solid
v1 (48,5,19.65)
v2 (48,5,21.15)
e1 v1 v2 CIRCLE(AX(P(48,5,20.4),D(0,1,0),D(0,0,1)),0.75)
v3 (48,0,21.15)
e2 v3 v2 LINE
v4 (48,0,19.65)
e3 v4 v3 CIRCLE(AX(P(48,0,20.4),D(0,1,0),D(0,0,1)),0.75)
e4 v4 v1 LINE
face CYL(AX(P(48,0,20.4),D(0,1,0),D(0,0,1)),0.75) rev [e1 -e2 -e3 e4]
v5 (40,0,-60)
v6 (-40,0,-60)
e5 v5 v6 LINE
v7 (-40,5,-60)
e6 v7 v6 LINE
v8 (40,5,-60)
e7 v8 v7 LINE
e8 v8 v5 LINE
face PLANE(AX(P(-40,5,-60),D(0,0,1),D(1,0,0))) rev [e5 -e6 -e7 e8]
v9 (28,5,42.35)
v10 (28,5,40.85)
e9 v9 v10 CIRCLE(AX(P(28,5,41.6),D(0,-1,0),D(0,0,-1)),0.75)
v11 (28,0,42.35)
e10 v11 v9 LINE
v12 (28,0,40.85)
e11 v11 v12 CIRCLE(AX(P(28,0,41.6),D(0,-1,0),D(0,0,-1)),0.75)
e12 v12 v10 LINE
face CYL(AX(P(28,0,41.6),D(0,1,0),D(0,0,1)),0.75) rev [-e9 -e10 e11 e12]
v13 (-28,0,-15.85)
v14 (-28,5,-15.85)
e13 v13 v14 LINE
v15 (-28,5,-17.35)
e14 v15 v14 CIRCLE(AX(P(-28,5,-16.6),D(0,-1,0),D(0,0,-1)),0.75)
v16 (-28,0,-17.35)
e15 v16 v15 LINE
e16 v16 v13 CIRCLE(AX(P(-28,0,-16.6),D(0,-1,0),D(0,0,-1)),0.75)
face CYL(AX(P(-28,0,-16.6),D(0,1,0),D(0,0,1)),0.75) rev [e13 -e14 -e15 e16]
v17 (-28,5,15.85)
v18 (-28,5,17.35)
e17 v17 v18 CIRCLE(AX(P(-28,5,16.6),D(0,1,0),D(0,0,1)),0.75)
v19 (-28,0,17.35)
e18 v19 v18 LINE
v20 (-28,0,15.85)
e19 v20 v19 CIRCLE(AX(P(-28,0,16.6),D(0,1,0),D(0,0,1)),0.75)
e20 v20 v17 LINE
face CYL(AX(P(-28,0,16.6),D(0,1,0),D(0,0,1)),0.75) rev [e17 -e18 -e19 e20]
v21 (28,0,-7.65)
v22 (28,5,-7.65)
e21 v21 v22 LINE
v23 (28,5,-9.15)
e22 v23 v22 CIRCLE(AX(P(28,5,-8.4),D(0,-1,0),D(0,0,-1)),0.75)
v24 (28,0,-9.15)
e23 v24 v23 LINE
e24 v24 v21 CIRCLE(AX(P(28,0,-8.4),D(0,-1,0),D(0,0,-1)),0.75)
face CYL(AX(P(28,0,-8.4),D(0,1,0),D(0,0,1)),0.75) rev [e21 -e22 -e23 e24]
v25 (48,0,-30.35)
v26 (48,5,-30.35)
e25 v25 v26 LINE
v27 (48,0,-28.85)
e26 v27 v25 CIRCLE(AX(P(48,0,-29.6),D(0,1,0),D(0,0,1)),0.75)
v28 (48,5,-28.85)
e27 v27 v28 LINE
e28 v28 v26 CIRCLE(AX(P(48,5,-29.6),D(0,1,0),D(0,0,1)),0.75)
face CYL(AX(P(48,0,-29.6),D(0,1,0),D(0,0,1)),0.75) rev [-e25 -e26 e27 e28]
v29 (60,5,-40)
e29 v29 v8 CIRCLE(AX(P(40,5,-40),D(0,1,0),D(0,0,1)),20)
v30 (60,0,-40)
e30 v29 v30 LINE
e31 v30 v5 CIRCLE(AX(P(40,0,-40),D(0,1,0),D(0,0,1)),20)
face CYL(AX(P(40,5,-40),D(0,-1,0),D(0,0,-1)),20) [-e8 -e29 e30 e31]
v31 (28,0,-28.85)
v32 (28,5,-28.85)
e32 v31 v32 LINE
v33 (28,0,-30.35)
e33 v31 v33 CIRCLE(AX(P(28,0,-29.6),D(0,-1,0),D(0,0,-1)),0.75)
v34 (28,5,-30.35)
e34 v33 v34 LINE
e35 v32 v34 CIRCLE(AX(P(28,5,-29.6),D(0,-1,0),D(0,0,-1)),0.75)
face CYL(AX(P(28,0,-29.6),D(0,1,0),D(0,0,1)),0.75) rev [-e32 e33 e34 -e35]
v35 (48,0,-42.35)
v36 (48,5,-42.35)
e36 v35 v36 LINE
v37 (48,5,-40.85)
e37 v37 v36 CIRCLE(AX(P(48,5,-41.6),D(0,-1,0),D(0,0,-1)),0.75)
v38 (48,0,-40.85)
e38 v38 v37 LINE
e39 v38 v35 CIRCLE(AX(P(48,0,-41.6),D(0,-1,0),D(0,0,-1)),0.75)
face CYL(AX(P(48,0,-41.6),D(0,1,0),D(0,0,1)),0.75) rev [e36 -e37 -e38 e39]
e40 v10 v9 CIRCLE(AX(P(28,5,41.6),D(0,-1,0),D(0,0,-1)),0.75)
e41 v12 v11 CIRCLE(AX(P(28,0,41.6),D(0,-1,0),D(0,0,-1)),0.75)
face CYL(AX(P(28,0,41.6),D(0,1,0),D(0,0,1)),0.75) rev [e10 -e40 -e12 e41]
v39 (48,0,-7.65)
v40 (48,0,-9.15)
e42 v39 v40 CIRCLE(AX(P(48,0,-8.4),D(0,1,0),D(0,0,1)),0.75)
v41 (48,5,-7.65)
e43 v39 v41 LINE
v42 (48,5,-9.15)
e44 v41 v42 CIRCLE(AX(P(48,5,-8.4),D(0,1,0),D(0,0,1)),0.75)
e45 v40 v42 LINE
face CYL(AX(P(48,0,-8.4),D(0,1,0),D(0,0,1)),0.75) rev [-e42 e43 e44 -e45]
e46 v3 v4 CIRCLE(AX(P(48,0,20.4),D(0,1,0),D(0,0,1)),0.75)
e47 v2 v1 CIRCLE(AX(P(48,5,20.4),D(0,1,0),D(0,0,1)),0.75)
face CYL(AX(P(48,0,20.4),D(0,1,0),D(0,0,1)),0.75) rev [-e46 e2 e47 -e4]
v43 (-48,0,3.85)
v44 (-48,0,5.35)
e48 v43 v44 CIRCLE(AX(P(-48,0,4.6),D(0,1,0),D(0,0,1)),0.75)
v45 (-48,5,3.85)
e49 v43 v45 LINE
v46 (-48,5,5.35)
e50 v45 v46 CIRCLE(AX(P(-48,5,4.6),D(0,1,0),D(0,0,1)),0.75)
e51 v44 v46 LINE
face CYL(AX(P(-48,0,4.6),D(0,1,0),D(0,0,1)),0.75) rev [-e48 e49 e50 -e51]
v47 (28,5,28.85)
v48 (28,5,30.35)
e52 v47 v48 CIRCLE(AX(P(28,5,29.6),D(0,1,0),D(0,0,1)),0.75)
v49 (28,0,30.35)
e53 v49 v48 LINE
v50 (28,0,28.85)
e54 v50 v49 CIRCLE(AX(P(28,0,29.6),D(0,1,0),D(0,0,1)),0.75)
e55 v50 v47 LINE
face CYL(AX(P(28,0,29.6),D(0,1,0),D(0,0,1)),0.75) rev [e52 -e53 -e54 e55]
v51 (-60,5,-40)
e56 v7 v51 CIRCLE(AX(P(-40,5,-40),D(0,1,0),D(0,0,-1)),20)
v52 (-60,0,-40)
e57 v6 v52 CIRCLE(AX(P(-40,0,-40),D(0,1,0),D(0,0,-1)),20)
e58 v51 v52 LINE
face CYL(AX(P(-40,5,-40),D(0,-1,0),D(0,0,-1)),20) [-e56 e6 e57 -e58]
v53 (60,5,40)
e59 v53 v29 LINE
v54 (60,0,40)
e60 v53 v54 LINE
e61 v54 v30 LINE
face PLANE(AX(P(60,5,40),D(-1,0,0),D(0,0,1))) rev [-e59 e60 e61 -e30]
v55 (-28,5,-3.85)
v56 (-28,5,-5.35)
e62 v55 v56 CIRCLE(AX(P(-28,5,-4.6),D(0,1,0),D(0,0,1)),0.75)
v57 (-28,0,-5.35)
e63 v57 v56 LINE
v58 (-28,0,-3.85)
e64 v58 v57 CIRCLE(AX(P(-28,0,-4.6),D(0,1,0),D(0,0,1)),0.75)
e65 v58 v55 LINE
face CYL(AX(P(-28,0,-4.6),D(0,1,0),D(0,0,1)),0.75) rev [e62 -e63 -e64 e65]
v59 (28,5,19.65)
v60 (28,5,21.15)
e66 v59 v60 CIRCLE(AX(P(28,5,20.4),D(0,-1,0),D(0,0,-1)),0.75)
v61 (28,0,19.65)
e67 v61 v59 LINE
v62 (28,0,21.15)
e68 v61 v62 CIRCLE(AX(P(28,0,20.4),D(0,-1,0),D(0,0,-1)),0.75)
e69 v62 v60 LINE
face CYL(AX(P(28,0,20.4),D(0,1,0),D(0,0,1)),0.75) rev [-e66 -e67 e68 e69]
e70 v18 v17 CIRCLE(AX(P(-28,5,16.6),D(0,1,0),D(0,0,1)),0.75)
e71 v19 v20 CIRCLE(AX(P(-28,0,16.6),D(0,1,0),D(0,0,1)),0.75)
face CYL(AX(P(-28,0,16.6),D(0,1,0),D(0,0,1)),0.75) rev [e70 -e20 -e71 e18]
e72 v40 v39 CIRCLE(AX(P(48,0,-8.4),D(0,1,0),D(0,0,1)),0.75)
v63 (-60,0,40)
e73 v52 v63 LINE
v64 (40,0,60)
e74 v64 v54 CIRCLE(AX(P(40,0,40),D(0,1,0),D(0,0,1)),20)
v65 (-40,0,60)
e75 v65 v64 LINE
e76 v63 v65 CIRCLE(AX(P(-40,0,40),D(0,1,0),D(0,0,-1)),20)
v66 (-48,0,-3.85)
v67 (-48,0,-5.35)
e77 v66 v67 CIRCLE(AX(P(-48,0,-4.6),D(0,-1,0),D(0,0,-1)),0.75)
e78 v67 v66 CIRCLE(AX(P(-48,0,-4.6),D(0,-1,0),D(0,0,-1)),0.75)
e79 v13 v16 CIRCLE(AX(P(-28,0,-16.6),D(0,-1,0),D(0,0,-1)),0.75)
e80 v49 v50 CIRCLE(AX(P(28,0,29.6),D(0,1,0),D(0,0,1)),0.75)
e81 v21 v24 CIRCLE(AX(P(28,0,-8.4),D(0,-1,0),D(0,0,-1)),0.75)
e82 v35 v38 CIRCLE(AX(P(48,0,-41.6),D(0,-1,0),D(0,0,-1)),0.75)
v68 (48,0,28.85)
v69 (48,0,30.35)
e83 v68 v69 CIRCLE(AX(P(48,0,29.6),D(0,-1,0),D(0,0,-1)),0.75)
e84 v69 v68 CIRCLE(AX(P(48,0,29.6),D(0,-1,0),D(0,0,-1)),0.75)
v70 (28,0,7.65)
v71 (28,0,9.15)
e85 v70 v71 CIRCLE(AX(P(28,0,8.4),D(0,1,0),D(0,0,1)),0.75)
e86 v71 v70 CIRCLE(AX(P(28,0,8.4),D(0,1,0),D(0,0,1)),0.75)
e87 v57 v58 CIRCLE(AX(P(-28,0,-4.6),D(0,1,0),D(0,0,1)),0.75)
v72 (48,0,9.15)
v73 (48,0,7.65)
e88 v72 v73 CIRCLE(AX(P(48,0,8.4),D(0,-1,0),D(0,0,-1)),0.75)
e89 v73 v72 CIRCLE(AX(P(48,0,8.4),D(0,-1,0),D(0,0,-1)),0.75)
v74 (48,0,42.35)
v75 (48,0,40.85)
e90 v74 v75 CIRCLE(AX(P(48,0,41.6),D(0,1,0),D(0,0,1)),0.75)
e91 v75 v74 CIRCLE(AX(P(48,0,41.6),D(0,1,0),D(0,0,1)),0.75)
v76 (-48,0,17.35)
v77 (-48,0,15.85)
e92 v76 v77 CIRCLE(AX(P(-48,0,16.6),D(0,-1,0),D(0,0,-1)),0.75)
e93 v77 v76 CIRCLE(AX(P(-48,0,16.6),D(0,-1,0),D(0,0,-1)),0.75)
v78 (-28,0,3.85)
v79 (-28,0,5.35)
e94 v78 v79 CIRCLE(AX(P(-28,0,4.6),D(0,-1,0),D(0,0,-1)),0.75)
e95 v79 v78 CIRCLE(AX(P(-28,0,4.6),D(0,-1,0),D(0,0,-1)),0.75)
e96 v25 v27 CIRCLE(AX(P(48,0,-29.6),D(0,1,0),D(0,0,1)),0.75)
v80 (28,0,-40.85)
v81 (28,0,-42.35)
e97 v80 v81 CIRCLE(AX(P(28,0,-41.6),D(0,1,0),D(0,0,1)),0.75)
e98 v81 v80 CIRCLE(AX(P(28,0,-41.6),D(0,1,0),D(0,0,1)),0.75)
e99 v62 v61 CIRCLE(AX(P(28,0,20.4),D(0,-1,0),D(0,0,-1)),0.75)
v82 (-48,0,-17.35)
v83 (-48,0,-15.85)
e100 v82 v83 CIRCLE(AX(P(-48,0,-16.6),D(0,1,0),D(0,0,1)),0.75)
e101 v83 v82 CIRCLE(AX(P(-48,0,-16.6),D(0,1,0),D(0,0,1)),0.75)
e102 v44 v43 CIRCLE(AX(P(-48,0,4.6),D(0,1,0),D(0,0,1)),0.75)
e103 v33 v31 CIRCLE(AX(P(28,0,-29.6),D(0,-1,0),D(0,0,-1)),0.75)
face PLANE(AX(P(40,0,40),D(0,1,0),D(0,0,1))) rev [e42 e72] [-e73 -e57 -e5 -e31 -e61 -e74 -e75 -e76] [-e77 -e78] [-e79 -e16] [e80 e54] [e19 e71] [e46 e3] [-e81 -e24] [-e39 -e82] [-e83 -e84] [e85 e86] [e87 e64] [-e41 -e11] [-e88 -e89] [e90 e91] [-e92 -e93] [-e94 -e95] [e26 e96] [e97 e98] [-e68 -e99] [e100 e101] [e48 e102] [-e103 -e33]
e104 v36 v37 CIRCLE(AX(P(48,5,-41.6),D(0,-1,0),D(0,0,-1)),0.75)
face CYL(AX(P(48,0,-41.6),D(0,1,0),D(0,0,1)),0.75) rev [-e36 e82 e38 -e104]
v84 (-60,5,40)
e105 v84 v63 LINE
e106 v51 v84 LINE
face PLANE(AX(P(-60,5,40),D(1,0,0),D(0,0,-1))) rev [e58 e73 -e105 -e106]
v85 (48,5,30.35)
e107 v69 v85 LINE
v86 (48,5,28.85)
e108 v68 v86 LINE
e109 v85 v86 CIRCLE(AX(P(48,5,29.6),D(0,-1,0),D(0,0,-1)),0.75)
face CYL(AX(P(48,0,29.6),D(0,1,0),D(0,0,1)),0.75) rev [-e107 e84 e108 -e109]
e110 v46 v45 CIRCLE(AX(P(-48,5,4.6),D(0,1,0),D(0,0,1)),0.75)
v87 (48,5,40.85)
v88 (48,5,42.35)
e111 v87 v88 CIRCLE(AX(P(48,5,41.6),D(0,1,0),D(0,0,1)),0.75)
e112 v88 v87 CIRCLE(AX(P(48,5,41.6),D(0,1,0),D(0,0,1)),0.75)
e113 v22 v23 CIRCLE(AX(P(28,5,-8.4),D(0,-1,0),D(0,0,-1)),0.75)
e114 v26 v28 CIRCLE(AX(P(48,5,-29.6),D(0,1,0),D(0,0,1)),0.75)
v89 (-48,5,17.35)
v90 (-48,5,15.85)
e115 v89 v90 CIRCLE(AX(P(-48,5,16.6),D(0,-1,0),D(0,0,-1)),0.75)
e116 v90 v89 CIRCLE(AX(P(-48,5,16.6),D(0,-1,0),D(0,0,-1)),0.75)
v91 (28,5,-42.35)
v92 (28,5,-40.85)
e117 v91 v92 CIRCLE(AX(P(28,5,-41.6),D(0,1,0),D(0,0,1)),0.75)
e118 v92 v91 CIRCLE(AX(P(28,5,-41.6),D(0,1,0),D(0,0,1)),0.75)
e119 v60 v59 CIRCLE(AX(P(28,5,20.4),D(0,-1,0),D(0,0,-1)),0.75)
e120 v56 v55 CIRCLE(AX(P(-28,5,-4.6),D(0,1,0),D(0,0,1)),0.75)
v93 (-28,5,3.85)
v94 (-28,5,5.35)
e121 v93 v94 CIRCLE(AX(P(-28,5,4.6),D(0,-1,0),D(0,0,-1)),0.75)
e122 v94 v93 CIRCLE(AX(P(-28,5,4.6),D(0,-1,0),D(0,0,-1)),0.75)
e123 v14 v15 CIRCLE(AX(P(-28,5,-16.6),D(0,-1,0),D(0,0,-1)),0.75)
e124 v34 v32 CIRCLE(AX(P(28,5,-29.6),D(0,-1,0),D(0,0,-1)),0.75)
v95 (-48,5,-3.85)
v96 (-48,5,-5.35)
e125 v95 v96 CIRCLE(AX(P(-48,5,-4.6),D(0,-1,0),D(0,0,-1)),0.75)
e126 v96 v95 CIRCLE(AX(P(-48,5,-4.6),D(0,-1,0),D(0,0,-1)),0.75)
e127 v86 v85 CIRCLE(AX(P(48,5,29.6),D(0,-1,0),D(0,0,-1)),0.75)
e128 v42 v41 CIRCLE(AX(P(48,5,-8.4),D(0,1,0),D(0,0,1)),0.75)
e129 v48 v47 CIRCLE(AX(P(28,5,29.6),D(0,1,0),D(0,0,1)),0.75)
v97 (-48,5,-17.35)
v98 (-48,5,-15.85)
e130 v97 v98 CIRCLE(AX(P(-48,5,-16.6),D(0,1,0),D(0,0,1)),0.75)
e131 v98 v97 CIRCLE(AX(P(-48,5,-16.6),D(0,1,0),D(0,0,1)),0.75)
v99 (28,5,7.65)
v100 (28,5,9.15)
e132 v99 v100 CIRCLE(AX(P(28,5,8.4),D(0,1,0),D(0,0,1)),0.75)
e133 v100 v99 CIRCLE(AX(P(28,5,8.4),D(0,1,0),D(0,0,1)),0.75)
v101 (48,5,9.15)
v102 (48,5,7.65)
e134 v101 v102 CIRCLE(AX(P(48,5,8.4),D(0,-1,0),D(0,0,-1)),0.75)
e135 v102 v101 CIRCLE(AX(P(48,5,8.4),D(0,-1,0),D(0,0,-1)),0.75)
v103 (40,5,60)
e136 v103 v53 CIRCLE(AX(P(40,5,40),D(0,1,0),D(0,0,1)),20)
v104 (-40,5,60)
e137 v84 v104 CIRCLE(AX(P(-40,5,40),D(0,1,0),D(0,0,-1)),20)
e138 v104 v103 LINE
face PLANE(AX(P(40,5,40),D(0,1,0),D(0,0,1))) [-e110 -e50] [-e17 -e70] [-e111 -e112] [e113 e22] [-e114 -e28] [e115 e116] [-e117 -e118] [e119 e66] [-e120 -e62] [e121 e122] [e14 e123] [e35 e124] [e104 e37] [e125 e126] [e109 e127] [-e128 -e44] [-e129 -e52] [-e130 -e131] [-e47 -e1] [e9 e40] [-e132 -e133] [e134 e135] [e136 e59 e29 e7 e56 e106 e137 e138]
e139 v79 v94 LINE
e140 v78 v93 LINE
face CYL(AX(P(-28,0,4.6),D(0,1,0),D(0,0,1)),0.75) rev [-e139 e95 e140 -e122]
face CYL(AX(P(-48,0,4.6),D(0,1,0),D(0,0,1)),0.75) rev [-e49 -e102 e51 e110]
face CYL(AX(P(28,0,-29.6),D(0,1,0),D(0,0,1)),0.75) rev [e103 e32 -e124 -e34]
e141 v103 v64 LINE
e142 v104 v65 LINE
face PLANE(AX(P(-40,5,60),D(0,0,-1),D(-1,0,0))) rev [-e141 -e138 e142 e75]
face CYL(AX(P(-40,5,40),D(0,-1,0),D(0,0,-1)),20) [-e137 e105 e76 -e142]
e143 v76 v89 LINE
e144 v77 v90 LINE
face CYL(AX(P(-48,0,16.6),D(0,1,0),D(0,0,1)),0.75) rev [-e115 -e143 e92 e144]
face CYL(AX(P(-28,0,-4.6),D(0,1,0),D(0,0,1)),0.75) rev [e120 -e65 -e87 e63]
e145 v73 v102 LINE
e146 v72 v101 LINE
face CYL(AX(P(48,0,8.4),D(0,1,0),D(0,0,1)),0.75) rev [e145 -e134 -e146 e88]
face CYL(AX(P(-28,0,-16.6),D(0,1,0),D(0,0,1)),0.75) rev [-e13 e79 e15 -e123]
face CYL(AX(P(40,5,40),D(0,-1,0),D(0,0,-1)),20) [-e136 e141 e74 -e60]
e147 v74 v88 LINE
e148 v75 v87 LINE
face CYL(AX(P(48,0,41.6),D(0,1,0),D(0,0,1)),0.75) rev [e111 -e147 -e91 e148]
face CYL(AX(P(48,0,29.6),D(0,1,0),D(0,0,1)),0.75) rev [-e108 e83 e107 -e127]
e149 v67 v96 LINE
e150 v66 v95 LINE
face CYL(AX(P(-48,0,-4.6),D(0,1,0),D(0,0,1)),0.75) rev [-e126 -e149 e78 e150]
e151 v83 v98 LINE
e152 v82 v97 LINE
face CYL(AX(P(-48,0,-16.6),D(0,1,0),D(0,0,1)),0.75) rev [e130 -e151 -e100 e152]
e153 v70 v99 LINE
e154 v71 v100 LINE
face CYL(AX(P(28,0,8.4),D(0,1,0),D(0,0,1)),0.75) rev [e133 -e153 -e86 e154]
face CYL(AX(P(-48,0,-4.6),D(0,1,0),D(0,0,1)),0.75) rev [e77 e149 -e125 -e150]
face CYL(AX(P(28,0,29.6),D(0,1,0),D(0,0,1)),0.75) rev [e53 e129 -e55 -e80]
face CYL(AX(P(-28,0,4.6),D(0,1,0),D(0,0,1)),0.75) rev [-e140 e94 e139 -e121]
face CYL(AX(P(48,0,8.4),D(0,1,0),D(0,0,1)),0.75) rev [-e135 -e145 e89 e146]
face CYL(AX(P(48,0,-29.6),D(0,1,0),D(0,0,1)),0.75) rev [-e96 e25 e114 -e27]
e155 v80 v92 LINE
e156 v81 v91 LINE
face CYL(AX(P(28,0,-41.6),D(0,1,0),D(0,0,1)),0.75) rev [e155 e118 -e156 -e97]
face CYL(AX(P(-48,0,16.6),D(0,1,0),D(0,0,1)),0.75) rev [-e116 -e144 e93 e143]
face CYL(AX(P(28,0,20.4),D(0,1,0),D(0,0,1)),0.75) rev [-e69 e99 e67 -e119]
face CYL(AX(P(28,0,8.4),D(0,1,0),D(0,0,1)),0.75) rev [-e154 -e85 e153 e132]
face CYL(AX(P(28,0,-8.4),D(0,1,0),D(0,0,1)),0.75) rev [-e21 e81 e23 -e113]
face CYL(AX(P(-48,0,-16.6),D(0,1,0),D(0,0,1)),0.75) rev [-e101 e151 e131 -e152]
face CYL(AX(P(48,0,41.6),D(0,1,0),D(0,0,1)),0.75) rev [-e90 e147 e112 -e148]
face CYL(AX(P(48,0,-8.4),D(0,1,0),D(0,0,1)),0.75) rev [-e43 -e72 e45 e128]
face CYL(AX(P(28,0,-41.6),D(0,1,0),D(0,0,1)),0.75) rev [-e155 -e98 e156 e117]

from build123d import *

# Parameters (mm, degrees)
BOSS_EXTRUDE1_DEPTH = 5
SKETCH4_R           = 0.75
CUT_EXTRUDE1_DEPTH  = 86


with BuildPart() as part:
    # Sketch1 → Boss-Extrude1 (new body)
    with BuildSketch(Plane(origin=(0, 0, 0), x_dir=(1, 0, 0), z_dir=(0, 1, 0))):
        with BuildLine():
            Line((-40, -60), (40, -60))
            ThreePointArc((40, -60), (54.142135624, -54.142135624), (60, -40))
            Line((60, -40), (60, 40))
            ThreePointArc((60, 40), (54.142135624, 54.142135624), (40, 60))
            Line((40, 60), (-40, 60))
            ThreePointArc((-40, 60), (-54.142135624, 54.142135624), (-60, 40))
            Line((-60, 40), (-60, -40))
            ThreePointArc((-60, -40), (-54.142135624, -54.142135624), (-40, -60))
        make_face()
    extrude(amount=BOSS_EXTRUDE1_DEPTH)

    # Sketch4 → Cut-Extrude1 (cut, through all)
    with BuildSketch(Plane(origin=(0, 5, 0), x_dir=(1, 0, 0), z_dir=(0, 1, 0))):
        with Locations(Location((-48, 16.6, 0), (0, 0, 270))):
            Circle(SKETCH4_R)
        with Locations(Location((-28, 16.6, 0), (0, 0, 90))):
            Circle(SKETCH4_R)
        with Locations(Location((-48, 4.6, 0), (0, 0, 90))):
            Circle(SKETCH4_R)
        with Locations(Location((-28, 4.6, 0), (0, 0, 270))):
            Circle(SKETCH4_R)
        with Locations(Location((-28, -4.6, 0), (0, 0, 90))):
            Circle(SKETCH4_R)
        with Locations(Location((-48, -4.6, 0), (0, 0, 270))):
            Circle(SKETCH4_R)
        with Locations(Location((-28, -16.6, 0), (0, 0, 270))):
            Circle(SKETCH4_R)
        with Locations(Location((-48, -16.6, 0), (0, 0, 90))):
            Circle(SKETCH4_R)
        with Locations(Location((28, 41.6, 0), (0, 0, 270))):
            Circle(SKETCH4_R)
        with Locations(Location((48, 41.6, 0), (0, 0, 90))):
            Circle(SKETCH4_R)
        with Locations(Location((28, 29.6, 0), (0, 0, 90))):
            Circle(SKETCH4_R)
        with Locations(Location((48, 29.6, 0), (0, 0, 270))):
            Circle(SKETCH4_R)
        with Locations(Location((48, 8.4, 0), (0, 0, 270))):
            Circle(SKETCH4_R)
        with Locations(Location((28, 8.4, 0), (0, 0, 90))):
            Circle(SKETCH4_R)
        with Locations(Location((28, -8.4, 0), (0, 0, 270))):
            Circle(SKETCH4_R)
        with Locations(Location((48, -8.4, 0), (0, 0, 90))):
            Circle(SKETCH4_R)
        with Locations(Location((28, -20.4, 0), (0, 0, 90))):
            Circle(SKETCH4_R)
        with Locations(Location((48, -20.4, 0), (0, 0, 270))):
            Circle(SKETCH4_R)
        with Locations(Location((48, -29.6, 0), (0, 0, 90))):
            Circle(SKETCH4_R)
        with Locations(Location((28, -29.6, 0), (0, 0, 270))):
            Circle(SKETCH4_R)
        with Locations(Location((48, -41.6, 0), (0, 0, 270))):
            Circle(SKETCH4_R)
        with Locations(Location((28, -41.6, 0), (0, 0, 90))):
            Circle(SKETCH4_R)
    extrude(amount=-CUT_EXTRUDE1_DEPTH, mode=Mode.SUBTRACT)


solid = part.part
